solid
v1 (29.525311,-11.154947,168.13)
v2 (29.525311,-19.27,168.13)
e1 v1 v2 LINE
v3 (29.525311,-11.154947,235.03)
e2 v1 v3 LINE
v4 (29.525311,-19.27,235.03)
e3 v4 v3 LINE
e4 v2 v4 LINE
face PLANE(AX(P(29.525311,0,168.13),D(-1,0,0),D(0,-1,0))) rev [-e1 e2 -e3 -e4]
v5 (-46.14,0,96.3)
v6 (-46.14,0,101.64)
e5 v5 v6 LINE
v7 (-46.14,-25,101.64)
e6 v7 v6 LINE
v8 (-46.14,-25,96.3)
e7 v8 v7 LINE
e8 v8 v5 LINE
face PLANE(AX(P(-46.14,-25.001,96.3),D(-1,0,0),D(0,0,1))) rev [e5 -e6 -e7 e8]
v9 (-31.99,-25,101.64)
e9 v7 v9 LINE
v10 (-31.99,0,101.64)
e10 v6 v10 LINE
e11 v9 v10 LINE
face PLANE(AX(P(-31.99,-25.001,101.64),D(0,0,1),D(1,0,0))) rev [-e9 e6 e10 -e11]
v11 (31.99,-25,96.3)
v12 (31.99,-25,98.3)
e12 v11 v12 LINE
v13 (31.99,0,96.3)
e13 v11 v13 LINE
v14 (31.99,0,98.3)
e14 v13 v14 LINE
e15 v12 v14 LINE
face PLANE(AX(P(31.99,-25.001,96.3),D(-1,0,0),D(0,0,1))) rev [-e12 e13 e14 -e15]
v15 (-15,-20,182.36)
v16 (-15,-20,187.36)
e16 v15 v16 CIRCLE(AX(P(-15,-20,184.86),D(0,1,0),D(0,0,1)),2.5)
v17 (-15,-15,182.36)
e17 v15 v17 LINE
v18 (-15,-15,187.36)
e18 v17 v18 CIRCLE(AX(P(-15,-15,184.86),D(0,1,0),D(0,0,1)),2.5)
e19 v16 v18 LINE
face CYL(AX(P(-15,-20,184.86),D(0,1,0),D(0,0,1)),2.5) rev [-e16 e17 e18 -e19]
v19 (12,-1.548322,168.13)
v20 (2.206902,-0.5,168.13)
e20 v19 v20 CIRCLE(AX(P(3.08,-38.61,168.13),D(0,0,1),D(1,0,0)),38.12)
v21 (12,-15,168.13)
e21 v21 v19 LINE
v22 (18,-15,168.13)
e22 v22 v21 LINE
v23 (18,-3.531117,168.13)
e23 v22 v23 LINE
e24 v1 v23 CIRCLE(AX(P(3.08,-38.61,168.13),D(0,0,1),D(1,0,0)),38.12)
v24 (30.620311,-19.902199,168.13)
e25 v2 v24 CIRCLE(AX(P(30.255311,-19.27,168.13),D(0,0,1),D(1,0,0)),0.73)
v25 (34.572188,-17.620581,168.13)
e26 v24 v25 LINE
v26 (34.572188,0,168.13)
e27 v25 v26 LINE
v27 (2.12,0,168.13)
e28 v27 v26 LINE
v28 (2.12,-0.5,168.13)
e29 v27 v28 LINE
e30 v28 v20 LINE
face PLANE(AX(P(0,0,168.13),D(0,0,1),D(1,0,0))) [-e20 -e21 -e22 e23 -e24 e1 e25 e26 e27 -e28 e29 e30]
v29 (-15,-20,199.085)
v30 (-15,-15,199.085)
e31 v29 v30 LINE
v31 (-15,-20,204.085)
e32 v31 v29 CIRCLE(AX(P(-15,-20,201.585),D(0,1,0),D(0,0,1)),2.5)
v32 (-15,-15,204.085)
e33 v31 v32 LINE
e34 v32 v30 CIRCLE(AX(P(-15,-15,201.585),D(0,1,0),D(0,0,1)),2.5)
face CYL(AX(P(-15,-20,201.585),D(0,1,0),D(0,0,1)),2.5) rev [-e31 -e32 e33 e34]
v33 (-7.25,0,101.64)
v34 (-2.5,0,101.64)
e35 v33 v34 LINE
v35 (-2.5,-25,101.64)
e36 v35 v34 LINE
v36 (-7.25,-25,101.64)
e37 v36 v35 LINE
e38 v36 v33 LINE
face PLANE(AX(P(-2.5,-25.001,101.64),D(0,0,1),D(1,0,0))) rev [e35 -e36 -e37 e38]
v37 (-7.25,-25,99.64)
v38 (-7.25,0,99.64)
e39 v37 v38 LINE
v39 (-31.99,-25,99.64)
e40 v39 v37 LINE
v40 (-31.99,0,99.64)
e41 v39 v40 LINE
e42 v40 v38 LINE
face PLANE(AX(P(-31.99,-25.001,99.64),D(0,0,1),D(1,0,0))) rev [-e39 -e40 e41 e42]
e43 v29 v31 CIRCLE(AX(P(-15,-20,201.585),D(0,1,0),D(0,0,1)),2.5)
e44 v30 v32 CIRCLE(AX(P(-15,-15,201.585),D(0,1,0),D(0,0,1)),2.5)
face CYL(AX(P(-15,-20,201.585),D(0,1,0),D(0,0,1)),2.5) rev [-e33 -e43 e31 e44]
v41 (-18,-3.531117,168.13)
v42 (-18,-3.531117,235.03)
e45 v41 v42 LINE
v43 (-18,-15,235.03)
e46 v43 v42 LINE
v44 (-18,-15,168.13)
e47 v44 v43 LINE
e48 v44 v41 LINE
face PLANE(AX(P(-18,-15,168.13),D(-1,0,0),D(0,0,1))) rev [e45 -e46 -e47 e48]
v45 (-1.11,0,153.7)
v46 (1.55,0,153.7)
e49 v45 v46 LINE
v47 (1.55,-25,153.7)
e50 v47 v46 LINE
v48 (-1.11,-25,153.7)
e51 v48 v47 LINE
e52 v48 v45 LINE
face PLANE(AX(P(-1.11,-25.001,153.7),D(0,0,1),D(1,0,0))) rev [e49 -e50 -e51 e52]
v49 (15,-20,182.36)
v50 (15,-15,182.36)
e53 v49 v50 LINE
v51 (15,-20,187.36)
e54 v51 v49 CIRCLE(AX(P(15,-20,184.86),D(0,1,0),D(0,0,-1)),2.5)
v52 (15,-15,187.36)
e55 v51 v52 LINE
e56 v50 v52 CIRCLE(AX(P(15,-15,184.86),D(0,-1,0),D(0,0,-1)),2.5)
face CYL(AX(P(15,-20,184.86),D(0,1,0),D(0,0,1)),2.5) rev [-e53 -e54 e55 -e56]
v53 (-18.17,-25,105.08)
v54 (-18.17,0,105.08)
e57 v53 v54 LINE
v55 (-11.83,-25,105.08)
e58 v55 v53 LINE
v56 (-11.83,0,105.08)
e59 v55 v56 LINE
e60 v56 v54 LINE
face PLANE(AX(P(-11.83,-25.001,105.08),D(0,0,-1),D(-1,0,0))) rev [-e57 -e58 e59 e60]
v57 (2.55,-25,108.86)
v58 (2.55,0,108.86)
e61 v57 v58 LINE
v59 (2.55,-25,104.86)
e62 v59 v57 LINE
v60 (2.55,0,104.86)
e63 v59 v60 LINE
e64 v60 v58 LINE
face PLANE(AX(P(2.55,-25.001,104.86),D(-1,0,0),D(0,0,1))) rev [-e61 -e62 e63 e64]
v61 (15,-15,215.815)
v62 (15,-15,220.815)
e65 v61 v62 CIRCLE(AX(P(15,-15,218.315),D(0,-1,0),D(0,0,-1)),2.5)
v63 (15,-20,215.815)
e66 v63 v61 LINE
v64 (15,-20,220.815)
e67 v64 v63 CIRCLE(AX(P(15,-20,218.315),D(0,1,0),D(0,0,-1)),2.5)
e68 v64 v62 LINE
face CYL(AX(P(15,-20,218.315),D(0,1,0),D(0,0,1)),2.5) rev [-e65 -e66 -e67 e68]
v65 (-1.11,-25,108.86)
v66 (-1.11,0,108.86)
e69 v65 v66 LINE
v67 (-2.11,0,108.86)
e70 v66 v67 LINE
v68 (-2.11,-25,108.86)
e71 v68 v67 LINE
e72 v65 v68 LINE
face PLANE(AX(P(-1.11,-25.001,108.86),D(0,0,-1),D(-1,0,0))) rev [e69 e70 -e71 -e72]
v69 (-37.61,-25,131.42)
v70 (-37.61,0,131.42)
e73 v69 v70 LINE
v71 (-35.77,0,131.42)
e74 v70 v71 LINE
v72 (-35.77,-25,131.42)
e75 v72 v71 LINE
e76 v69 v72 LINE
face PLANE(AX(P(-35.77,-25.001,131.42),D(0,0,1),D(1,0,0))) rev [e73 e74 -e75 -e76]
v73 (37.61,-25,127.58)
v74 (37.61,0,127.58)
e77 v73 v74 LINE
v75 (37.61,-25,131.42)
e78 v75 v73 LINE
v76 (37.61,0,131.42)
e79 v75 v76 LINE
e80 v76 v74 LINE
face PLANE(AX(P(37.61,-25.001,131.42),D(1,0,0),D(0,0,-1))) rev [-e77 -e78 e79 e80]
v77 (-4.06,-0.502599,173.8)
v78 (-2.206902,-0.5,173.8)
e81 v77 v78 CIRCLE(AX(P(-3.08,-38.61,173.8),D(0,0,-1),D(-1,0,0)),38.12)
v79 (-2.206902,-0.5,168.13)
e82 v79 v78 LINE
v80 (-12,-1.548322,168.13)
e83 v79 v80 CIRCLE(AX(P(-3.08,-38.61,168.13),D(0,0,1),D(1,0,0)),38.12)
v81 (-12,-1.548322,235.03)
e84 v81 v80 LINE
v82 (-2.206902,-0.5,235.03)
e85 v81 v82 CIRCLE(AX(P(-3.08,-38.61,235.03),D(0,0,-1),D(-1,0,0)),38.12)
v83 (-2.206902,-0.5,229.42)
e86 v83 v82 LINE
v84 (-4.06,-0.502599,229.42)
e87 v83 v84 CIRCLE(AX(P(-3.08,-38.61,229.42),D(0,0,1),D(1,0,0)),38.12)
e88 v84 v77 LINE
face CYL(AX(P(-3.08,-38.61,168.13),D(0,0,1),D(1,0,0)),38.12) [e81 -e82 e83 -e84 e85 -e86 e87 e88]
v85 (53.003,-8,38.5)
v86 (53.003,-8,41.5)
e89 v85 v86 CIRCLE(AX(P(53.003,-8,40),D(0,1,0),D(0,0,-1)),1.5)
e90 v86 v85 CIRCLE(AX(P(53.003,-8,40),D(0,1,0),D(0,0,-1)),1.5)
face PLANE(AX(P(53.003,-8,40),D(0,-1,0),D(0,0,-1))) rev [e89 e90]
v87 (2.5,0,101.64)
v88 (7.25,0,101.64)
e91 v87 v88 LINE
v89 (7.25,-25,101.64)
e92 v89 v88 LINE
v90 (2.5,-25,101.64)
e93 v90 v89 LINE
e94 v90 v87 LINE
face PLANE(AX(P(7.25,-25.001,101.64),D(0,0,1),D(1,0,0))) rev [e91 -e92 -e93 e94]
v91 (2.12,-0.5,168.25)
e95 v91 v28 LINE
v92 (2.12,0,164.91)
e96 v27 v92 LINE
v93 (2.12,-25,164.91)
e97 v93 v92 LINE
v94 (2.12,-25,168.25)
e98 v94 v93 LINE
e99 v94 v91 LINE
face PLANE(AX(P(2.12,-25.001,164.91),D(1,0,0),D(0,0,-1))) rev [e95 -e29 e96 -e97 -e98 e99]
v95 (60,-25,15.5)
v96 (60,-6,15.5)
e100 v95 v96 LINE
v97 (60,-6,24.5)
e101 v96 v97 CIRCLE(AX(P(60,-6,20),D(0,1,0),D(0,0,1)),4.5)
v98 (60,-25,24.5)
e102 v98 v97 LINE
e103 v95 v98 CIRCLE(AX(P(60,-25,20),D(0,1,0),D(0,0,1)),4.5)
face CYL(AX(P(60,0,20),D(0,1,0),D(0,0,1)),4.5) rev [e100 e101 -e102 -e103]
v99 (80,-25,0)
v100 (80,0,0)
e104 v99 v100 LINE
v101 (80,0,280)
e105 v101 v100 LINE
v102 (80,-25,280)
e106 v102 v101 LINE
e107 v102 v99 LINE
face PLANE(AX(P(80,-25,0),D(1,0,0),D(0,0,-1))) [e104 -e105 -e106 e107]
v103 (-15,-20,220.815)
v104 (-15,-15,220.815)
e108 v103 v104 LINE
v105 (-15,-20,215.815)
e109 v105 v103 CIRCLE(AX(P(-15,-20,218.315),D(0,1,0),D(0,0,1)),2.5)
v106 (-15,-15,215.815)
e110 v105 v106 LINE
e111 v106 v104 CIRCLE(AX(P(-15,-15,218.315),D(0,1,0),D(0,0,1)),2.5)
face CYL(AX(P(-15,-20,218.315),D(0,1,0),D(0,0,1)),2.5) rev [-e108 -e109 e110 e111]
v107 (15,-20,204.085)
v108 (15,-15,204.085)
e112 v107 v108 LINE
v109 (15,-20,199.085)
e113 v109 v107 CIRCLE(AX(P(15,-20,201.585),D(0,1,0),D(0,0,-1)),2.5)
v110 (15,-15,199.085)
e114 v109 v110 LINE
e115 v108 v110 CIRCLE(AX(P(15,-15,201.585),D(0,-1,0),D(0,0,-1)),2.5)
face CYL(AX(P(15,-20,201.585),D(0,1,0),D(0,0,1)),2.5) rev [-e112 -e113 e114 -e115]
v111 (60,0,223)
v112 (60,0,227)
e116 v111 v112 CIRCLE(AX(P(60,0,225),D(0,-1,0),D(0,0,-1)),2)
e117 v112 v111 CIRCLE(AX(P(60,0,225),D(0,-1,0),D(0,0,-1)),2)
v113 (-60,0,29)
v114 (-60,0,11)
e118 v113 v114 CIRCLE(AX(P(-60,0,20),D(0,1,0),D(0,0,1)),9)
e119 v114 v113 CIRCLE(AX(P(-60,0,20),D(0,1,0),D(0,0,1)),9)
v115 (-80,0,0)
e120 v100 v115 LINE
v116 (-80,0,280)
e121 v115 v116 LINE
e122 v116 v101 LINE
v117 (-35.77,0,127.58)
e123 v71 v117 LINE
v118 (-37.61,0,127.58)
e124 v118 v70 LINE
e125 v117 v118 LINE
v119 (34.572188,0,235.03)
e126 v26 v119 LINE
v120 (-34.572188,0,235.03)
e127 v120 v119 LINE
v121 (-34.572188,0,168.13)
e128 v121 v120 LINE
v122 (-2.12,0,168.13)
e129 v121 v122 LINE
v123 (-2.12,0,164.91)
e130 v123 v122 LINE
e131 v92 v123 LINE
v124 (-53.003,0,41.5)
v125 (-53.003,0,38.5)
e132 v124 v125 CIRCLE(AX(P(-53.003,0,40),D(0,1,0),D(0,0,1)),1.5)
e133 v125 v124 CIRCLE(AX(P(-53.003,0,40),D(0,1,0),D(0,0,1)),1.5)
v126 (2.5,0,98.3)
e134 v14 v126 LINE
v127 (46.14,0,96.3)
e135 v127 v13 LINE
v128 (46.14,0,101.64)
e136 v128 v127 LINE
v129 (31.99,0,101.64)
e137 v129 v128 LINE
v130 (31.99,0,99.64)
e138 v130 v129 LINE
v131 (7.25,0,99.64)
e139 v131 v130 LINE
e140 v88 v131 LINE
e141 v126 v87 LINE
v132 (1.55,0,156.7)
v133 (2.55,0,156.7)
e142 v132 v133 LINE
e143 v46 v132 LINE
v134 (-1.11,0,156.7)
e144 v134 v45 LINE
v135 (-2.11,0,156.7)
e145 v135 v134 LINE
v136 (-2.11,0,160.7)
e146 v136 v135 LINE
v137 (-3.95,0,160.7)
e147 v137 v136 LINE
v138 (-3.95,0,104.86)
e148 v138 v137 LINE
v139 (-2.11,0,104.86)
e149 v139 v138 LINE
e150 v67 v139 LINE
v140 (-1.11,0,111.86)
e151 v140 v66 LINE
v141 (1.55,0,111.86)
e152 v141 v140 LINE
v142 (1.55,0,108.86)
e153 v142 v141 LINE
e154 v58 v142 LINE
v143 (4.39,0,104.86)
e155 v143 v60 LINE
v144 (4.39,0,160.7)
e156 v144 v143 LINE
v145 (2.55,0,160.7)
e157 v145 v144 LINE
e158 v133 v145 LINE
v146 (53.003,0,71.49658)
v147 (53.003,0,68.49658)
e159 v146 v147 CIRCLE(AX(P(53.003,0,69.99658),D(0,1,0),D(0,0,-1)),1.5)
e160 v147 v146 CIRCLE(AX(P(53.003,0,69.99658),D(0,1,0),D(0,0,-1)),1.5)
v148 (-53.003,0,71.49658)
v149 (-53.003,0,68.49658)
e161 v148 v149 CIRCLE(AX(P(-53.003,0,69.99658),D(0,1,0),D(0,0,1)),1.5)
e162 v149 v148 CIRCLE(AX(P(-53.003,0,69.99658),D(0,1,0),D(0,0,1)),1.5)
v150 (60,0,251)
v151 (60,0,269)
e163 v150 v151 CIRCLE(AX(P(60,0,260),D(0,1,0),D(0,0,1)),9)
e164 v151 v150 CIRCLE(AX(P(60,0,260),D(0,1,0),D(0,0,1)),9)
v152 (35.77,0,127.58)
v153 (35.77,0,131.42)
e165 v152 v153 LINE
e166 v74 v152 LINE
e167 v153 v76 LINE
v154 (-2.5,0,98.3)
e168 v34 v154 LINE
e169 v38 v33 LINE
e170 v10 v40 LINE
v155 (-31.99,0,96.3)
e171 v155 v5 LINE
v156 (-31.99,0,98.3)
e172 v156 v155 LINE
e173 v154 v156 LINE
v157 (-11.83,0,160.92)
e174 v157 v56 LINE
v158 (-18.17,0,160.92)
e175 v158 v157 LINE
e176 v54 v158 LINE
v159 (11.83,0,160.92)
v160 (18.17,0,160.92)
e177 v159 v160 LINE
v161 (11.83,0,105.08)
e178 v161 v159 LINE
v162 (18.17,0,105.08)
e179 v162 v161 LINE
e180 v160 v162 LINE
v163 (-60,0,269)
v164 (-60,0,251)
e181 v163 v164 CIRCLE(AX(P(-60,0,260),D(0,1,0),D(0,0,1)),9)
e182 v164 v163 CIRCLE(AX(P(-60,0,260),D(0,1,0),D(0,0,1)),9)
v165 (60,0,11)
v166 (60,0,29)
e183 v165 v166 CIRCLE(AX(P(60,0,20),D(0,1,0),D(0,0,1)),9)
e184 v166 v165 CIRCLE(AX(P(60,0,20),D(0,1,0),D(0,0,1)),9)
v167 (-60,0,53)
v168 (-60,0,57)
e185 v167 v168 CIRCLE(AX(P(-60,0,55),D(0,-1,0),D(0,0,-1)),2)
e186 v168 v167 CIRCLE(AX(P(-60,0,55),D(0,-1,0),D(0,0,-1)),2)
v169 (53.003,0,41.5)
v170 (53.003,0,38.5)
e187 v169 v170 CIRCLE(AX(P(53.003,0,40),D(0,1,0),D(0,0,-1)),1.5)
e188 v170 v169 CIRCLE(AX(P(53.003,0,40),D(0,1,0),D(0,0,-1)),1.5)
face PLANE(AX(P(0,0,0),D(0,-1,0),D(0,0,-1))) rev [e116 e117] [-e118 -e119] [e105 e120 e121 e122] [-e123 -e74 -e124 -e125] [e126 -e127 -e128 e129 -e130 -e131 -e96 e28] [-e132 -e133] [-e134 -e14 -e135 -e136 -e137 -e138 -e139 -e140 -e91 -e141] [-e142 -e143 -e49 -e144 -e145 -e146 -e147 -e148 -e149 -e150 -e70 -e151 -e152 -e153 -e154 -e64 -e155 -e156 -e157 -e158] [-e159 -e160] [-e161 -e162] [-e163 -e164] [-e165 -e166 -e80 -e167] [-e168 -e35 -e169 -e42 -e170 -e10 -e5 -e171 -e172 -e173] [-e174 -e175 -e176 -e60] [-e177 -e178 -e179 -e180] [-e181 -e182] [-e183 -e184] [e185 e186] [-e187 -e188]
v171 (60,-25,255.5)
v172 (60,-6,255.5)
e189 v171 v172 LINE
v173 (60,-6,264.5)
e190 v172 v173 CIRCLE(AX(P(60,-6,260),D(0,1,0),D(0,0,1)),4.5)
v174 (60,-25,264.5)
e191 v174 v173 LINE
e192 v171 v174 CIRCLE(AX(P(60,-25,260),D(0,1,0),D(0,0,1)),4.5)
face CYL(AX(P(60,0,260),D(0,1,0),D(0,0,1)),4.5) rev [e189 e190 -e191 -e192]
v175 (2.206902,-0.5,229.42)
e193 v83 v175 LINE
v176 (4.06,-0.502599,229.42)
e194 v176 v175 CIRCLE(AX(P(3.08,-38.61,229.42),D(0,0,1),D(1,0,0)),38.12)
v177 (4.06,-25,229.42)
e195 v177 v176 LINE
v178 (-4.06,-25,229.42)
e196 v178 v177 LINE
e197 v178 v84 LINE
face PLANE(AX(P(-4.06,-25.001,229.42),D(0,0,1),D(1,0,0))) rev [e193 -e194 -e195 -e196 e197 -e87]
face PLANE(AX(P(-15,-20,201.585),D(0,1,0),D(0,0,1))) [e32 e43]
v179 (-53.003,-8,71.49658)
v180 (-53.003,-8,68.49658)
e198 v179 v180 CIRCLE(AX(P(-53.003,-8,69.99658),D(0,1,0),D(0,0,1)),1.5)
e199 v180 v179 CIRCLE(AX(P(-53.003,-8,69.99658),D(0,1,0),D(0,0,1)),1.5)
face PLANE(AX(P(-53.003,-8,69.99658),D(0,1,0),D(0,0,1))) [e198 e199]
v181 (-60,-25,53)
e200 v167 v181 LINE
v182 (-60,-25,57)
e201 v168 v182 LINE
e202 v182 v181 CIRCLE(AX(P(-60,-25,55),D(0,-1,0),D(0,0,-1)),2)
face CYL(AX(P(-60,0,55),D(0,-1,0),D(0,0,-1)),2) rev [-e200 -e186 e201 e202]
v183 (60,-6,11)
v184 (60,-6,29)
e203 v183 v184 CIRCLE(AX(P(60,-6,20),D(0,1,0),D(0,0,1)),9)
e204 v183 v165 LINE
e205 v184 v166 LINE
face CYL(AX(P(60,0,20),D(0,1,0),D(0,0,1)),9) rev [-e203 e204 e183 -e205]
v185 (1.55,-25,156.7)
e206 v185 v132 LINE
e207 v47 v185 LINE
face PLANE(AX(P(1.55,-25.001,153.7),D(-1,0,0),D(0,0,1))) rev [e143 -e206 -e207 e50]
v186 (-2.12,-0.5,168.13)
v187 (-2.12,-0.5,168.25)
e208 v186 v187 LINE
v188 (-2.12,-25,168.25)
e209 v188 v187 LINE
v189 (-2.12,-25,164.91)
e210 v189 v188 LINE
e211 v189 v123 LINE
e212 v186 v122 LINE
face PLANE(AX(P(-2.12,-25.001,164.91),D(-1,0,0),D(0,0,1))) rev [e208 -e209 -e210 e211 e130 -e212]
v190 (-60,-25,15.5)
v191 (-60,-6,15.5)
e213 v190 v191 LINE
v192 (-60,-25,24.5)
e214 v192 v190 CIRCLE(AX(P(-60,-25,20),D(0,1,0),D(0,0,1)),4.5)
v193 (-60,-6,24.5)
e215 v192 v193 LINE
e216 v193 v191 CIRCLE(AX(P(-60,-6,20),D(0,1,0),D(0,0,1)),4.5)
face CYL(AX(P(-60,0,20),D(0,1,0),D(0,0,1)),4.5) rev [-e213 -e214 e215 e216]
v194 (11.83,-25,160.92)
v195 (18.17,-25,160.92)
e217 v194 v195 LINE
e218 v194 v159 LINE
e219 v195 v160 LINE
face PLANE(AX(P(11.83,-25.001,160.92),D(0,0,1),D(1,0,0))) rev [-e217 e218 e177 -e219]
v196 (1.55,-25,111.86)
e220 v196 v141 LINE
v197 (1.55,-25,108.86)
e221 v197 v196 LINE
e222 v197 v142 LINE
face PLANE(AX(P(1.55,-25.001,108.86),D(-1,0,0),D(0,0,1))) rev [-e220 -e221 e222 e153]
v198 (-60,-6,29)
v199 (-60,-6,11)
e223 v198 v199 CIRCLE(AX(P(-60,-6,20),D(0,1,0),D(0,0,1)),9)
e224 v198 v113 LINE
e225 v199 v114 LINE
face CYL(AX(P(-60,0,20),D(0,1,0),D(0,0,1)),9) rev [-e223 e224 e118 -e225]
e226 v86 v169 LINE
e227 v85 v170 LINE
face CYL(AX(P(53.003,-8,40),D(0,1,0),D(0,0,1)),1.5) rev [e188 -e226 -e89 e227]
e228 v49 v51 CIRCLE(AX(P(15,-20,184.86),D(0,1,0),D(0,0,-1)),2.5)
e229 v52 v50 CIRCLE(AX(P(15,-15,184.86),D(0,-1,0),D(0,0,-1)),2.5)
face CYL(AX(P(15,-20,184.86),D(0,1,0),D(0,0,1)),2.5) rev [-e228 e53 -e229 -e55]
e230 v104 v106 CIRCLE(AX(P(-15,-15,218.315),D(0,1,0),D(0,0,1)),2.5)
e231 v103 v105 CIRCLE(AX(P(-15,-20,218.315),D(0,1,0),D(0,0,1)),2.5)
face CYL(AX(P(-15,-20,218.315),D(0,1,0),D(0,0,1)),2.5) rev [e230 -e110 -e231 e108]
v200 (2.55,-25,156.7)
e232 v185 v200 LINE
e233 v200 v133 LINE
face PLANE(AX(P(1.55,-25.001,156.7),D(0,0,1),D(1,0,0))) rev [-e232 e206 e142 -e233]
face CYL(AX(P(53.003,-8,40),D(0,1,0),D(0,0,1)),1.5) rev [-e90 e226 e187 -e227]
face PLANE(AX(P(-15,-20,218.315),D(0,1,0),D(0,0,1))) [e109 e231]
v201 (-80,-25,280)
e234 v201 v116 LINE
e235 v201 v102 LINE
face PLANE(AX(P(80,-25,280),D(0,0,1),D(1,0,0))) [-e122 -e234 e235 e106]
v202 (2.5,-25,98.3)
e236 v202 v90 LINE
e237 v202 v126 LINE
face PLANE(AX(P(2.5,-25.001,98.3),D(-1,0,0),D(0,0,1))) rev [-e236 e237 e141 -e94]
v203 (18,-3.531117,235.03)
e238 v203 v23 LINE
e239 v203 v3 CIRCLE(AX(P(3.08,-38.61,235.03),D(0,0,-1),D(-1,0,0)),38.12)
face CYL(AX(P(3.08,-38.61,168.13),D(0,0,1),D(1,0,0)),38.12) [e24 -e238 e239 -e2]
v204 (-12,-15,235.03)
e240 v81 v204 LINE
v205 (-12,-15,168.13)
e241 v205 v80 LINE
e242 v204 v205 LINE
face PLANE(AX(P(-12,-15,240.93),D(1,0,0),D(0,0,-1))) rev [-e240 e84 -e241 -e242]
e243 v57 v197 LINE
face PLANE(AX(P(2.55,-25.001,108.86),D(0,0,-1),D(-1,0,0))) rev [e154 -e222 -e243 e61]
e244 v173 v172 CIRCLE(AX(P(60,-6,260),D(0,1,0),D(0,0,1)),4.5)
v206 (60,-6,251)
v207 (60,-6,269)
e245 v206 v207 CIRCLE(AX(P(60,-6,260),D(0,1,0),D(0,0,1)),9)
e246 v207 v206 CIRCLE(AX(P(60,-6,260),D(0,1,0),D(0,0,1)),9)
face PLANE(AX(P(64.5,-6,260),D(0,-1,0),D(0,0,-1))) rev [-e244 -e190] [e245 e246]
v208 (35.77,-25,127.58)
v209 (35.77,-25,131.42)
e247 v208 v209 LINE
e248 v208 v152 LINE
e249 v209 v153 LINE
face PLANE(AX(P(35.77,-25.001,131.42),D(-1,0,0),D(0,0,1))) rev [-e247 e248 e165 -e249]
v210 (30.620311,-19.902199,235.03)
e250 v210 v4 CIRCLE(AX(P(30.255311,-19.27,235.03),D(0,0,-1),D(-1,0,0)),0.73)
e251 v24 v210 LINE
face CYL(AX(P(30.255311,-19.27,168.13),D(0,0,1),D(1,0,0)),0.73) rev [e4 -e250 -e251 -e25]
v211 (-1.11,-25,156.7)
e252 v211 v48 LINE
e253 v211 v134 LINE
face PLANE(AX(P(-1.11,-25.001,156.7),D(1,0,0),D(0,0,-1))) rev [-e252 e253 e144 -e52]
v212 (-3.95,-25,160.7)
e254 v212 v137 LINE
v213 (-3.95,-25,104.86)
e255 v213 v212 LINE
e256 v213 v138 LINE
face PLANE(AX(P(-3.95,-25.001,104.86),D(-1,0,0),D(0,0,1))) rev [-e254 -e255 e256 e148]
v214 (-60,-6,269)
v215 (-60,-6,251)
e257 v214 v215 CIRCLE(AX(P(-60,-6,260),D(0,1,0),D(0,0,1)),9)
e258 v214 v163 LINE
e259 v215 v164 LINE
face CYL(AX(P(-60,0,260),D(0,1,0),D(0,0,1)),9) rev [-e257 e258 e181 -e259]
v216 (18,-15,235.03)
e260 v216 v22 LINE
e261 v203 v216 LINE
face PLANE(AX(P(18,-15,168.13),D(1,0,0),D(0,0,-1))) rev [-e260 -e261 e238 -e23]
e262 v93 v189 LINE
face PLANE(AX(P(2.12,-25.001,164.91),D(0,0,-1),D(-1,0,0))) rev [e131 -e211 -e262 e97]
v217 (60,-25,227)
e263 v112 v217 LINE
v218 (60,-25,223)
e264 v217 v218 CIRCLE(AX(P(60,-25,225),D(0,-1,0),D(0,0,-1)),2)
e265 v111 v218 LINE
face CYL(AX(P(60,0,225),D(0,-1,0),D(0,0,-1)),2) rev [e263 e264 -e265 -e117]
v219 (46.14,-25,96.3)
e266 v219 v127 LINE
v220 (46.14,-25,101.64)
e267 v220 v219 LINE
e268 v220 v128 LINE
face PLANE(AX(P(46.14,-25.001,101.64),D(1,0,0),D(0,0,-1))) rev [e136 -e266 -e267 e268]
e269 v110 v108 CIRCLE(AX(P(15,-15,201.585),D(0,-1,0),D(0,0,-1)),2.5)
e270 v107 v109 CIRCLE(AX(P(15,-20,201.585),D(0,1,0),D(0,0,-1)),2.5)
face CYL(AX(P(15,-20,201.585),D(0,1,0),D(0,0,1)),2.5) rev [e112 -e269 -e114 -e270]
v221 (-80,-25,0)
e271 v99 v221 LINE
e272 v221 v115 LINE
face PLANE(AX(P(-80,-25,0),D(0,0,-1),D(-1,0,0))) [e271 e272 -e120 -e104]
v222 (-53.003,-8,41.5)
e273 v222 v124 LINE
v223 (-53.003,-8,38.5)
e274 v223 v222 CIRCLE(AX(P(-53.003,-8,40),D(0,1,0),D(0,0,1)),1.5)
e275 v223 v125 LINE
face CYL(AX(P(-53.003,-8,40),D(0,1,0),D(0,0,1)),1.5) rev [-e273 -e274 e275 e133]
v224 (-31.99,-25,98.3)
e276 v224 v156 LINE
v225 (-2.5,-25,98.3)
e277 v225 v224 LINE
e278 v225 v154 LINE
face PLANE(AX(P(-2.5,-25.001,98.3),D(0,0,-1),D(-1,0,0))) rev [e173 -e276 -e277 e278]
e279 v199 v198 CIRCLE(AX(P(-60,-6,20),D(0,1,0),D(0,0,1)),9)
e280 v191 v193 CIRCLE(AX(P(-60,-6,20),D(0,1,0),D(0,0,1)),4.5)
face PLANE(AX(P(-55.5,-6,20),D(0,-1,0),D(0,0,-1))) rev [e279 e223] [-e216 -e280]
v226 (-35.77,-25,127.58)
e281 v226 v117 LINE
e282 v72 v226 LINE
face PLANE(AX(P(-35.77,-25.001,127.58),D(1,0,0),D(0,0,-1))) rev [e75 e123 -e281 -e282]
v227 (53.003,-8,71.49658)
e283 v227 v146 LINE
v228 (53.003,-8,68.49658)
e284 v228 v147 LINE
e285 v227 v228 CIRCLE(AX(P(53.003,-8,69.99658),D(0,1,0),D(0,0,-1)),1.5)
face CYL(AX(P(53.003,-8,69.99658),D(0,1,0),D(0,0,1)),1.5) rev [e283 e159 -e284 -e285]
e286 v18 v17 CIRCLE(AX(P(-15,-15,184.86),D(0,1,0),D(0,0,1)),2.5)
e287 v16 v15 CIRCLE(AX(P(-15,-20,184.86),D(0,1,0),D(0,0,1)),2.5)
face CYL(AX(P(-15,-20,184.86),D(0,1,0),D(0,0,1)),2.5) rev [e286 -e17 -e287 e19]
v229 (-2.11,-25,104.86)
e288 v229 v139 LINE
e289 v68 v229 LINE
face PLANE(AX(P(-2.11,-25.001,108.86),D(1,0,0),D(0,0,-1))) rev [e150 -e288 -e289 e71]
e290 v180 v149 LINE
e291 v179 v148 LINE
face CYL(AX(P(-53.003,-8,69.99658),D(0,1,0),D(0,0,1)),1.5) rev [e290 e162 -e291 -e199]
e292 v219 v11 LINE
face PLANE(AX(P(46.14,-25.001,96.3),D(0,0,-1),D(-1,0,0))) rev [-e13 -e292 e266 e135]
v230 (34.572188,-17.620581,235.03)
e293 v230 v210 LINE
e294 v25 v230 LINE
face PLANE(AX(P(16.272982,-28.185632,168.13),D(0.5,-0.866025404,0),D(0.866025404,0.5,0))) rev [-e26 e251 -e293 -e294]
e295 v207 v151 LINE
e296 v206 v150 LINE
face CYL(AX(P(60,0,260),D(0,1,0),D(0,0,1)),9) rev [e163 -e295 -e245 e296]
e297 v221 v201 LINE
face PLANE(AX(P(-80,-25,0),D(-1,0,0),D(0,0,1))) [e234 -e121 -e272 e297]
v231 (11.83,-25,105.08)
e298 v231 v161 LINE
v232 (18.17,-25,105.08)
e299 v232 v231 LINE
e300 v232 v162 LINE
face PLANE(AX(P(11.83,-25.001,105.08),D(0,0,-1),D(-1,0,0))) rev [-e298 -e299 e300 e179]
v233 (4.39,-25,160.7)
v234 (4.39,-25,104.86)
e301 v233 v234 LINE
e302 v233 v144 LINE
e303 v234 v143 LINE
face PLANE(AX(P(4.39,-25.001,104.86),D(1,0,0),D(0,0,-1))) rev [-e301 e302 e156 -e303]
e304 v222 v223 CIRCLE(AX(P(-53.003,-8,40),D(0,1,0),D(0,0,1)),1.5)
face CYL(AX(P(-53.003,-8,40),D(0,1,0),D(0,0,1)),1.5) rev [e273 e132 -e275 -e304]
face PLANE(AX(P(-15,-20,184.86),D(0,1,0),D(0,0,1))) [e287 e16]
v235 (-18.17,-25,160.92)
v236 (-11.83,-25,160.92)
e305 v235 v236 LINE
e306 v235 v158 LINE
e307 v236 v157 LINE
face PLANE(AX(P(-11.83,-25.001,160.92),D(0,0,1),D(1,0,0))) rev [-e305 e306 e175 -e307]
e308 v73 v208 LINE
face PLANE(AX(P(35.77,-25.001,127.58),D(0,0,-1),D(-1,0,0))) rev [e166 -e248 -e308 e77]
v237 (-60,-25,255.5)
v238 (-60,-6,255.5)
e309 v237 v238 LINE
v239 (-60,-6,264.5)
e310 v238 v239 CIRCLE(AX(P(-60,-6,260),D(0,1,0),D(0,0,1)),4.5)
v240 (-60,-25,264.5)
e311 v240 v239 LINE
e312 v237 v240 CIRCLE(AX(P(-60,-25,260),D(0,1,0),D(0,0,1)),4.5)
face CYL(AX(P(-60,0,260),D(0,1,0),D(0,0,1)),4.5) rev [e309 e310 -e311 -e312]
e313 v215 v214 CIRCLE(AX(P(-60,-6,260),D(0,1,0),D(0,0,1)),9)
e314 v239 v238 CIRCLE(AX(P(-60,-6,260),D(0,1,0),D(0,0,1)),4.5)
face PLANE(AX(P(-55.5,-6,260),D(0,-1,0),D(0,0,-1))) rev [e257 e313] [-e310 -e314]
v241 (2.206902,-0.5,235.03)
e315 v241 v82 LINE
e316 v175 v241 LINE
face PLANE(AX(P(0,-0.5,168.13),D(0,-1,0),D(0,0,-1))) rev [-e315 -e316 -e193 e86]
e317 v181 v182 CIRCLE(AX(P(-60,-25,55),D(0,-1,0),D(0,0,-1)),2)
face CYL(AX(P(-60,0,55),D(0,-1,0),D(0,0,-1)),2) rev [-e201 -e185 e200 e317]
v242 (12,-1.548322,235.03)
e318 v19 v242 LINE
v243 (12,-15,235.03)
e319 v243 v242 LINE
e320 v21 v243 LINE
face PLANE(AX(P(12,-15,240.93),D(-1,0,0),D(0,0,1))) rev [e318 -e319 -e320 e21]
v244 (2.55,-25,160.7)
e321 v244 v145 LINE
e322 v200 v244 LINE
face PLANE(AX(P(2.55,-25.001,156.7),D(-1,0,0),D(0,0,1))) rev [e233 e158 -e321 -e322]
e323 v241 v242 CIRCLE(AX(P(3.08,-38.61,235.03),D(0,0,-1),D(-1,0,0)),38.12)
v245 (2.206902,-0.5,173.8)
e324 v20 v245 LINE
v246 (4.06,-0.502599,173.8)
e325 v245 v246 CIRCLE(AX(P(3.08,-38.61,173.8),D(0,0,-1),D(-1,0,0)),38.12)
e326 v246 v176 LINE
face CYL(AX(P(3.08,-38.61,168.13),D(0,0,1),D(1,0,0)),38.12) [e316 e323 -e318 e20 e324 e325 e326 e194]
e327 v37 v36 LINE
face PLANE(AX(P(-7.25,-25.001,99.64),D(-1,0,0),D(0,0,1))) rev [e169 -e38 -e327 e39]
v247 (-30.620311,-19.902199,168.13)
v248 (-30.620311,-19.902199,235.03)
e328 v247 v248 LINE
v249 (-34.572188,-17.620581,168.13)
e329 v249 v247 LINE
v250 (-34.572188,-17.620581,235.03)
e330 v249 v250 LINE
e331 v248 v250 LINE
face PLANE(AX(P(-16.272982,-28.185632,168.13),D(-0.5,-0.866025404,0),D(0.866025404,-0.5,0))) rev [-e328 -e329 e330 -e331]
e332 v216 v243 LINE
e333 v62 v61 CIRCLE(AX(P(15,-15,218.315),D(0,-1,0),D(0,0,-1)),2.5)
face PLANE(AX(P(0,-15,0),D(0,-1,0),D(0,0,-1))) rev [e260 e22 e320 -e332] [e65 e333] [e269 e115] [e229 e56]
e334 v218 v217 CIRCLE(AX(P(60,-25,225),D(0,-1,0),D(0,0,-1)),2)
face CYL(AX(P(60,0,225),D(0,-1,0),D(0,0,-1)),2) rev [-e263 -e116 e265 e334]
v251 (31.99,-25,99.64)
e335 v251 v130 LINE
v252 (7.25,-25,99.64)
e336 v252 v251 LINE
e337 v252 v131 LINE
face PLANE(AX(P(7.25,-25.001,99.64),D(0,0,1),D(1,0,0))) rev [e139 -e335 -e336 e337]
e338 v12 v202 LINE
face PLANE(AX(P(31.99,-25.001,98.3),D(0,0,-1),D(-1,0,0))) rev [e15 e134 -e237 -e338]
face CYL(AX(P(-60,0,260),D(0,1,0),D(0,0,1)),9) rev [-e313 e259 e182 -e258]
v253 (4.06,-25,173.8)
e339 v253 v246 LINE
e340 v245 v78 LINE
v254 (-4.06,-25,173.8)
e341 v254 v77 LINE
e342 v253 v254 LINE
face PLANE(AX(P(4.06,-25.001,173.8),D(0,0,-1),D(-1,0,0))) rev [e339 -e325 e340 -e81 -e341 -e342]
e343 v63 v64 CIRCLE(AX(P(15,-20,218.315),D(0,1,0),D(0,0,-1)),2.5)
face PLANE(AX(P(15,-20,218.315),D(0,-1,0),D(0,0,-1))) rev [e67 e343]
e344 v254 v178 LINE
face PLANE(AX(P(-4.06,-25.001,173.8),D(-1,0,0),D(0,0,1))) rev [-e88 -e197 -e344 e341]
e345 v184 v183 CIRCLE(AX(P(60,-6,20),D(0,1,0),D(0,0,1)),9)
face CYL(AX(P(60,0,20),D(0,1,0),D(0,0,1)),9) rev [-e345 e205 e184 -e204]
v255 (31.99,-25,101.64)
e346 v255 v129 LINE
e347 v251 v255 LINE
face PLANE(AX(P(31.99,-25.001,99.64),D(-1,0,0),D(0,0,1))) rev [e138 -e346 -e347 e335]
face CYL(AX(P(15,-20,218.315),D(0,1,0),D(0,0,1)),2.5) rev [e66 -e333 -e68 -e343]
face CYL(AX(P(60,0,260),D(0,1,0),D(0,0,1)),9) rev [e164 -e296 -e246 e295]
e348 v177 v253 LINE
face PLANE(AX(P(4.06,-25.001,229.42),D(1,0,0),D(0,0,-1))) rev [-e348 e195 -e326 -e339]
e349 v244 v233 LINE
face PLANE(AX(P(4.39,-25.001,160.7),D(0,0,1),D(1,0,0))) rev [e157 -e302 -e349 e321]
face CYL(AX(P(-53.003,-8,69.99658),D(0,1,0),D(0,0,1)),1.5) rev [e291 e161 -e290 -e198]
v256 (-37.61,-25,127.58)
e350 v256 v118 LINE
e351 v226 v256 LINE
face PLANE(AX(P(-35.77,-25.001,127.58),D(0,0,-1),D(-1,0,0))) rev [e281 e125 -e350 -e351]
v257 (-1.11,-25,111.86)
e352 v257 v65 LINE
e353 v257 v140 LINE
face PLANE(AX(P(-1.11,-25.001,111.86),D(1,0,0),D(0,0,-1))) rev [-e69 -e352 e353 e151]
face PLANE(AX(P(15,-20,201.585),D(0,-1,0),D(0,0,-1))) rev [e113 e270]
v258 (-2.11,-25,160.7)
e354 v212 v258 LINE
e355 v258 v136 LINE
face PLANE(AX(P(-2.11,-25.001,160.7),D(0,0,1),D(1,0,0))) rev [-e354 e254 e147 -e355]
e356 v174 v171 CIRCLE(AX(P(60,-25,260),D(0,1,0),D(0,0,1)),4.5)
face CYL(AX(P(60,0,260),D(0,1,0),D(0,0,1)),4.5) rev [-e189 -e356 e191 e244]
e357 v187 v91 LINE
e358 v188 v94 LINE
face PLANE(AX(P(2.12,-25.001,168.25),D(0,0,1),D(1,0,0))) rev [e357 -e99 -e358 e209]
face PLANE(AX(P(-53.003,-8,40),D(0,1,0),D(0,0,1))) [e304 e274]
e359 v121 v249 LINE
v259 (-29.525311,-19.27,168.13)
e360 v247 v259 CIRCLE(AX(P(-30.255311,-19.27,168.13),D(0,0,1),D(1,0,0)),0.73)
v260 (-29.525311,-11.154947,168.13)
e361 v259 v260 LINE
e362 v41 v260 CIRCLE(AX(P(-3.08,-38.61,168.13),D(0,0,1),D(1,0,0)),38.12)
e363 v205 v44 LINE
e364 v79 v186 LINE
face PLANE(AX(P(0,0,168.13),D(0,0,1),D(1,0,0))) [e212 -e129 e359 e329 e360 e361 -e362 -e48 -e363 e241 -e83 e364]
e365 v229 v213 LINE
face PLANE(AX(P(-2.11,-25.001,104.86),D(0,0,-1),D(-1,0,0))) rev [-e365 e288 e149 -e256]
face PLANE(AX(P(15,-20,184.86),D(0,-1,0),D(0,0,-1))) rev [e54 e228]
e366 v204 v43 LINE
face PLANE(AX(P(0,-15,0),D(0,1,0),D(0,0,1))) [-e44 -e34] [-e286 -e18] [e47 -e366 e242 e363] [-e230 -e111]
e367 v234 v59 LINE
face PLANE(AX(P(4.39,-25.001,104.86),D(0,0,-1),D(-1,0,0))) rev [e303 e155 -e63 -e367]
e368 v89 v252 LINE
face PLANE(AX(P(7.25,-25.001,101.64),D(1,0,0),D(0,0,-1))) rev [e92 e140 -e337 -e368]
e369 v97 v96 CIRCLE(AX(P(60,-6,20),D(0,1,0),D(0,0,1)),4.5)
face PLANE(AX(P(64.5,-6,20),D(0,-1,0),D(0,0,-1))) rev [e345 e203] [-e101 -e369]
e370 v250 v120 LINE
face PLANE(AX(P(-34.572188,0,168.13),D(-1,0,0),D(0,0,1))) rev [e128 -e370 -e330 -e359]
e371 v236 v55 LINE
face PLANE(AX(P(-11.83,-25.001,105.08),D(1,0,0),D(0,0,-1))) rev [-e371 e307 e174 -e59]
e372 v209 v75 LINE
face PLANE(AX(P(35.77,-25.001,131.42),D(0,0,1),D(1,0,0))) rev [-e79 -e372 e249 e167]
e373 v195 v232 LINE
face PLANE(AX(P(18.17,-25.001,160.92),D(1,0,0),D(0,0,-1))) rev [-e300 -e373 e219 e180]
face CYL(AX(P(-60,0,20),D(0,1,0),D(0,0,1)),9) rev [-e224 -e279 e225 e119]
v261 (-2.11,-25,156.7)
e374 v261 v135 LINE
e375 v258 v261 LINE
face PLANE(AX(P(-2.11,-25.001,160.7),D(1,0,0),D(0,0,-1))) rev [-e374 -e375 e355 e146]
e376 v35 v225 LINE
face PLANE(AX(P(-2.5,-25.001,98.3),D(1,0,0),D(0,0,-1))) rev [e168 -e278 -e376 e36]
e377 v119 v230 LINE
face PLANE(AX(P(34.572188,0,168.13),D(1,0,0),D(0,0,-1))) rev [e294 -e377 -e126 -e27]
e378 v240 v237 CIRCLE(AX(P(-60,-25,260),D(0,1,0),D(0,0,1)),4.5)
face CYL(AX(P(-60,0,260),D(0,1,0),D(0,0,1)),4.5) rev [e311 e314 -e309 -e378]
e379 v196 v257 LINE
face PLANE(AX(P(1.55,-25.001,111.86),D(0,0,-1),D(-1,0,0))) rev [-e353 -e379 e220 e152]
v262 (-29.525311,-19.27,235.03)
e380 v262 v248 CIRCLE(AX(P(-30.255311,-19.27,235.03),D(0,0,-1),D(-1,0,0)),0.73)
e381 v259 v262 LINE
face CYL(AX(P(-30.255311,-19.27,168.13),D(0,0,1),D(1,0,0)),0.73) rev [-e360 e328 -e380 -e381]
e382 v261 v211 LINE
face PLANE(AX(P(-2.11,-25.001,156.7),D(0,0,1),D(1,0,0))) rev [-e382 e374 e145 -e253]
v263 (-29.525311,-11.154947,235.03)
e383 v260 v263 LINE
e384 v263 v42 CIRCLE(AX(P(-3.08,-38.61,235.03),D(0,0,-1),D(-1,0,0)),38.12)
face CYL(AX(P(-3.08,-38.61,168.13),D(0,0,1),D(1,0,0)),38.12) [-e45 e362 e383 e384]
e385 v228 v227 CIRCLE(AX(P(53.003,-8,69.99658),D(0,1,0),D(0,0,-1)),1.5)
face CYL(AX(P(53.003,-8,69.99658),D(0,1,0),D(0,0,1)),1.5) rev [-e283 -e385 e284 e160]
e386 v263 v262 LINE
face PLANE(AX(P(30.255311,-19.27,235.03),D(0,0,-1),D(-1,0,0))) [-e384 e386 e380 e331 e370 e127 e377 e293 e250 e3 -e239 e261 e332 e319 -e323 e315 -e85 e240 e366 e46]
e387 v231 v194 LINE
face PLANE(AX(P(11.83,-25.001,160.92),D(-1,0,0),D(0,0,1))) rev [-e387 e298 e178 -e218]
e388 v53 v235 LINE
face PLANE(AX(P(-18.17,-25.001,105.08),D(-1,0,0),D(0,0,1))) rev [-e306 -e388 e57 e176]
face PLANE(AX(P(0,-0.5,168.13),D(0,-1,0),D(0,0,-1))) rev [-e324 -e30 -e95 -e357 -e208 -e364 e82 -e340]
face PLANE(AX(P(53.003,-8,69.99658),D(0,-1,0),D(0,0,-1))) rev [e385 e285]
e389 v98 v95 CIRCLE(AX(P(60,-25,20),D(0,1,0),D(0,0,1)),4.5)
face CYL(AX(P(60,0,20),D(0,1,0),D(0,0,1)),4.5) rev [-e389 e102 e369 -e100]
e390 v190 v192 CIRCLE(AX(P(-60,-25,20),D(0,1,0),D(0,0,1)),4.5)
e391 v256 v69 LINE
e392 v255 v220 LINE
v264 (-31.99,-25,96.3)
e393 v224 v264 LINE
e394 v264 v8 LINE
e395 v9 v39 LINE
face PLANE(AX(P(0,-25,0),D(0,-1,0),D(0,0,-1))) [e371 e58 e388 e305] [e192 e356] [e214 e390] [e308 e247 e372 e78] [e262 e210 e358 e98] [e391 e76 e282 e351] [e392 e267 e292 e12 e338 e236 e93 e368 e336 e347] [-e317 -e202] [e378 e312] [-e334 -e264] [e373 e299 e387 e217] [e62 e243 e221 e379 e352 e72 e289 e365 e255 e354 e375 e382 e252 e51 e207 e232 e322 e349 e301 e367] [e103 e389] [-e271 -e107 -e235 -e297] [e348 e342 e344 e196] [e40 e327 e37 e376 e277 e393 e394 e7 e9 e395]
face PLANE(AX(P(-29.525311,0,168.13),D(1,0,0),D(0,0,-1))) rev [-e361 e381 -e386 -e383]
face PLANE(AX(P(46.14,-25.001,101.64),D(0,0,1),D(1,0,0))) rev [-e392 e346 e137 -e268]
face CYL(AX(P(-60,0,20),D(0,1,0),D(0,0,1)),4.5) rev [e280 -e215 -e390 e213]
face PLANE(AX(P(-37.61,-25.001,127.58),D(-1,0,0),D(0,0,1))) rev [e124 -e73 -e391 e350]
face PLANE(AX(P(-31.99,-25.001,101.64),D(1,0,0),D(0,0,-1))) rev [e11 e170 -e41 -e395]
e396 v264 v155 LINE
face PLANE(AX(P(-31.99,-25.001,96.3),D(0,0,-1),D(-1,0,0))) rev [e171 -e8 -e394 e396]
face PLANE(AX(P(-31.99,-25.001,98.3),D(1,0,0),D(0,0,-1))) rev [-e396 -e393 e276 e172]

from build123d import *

# Parameters (mm, degrees)
SKETCH1_W                                        = 160
SKETCH1_H                                        = 280
BOSS_EXTRUDE1_DEPTH                              = 25
CBORE_FOR_M8_PAN_HEAD_MACHINE_SCREW1_D           = 9
CBORE_FOR_M8_PAN_HEAD_MACHINE_SCREW1_CBORE_D     = 18
CBORE_FOR_M8_PAN_HEAD_MACHINE_SCREW1_CBORE_DEPTH = 6
CUT_EXTRUDE2_DEPTH                               = 72.8
CUT_EXTRUDE4_REACH                               = 294.276
SKETCH_5_W                                       = 4.24
SKETCH_5_H                                       = 3.34
SKETCH_5_W_2                                     = 8.12
SKETCH_5_H_2                                     = 55.62
SKETCH_5_W_3                                     = 1.84
SKETCH_5_H_3                                     = 3.84
SKETCH_5_W_4                                     = 6.34
SKETCH_5_H_4                                     = 55.84
SKETCH_6_W                                       = 6
SKETCH_6_H                                       = 72.8
CUT_EXTRUDE5_DEPTH                               = 15
EXTRUDE_1_DEPTH                                  = 5.9
SKETCH10_R                                       = 2.5
CUT_EXTRUDE6_DEPTH                               = 20
SKETCH13_R                                       = 1.5
CUT_EXTRUDE7_DEPTH                               = 8
SKETCH14_R                                       = 2
CUT_EXTRUDE8_DEPTH                               = 293.275554914


with BuildPart() as part:
    # Sketch1 → Boss-Extrude1 (new body)
    with BuildSketch(Plane(origin=(0, 0, 0), x_dir=(1, 0, 0), z_dir=(0, 1, 0))):
        with Locations((0, -140)):
            Rectangle(SKETCH1_W, SKETCH1_H)
    extrude(amount=-BOSS_EXTRUDE1_DEPTH)

    # CBORE for M8 Pan Head Machine Screw1 (through all)
    with Locations(Plane(origin=(0, 0, 0), x_dir=(1, 0, 0), z_dir=(0, 1, 0))):
        with Locations((-60, -260), (60, -260), (60, -20), (-60, -20)):
            CounterBoreHole(CBORE_FOR_M8_PAN_HEAD_MACHINE_SCREW1_D / 2, CBORE_FOR_M8_PAN_HEAD_MACHINE_SCREW1_CBORE_D / 2, CBORE_FOR_M8_PAN_HEAD_MACHINE_SCREW1_CBORE_DEPTH)

    # Sketch4 → Cut-Extrude2 (cut)
    with BuildSketch(Plane.XY.offset(240.93)):
        with BuildLine():
            ThreePointArc((29.525310886, -11.154947057), (16.931588105, -3.095666176), (2.206902067, -0.5))
            Line((2.206902067, -0.5), (-2.206902067, -0.5))
            ThreePointArc((-2.206902067, -0.5), (-16.931588105, -3.095666176), (-29.525310886, -11.154947057))
            Line((-29.525310886, -11.154947057), (-29.525310886, -19.27))
            ThreePointArc((-29.525310886, -19.27), (-29.890310886, -19.902198545), (-30.620310886, -19.902198545))
            Line((-30.620310886, -19.902198545), (-34.572188183, -17.620581124))
            Line((-34.572188183, -17.620581124), (-34.572188183, 0))
            Line((-34.572188183, 0), (34.572188183, 0))
            Line((34.572188183, 0), (34.572188183, -17.620581124))
            Line((34.572188183, -17.620581124), (30.620310886, -19.902198545))
            ThreePointArc((30.620310886, -19.902198545), (29.890310886, -19.902198545), (29.525310886, -19.27))
            Line((29.525310886, -19.27), (29.525310886, -11.154947057))
        make_face()
    extrude(amount=-CUT_EXTRUDE2_DEPTH, mode=Mode.SUBTRACT)

    # 草图5 → Cut-Extrude4 (cut, up to next)
    with BuildSketch(Plane(origin=(0, 0, 0), x_dir=(1, 0, 0), z_dir=(0, 1, 0)), mode=Mode.PRIVATE) as cut_extrude4_sk1:
        with Locations((0, -166.58)):
            Rectangle(SKETCH_5_W, SKETCH_5_H)
    cut_extrude4_tool1 = extrude(cut_extrude4_sk1.sketch, amount=-CUT_EXTRUDE4_REACH, mode=Mode.PRIVATE) & part.part
    # 草图5 → Cut-Extrude4 (cut, up to next)
    with BuildSketch(Plane(origin=(0, 0, 0), x_dir=(1, 0, 0), z_dir=(0, 1, 0)), mode=Mode.PRIVATE) as cut_extrude4_sk2:
        with Locations((0, -201.61)):
            Rectangle(SKETCH_5_W_2, SKETCH_5_H_2)
    cut_extrude4_tool2 = extrude(cut_extrude4_sk2.sketch, amount=-CUT_EXTRUDE4_REACH, mode=Mode.PRIVATE) & part.part
    # 草图5 → Cut-Extrude4 (cut, up to next)
    with BuildSketch(Plane(origin=(0, 0, 0), x_dir=(1, 0, 0), z_dir=(0, 1, 0)), mode=Mode.PRIVATE) as cut_extrude4_sk3:
        with Locations((36.69, -129.5)):
            Rectangle(SKETCH_5_W_3, SKETCH_5_H_3)
    cut_extrude4_tool3 = extrude(cut_extrude4_sk3.sketch, amount=-CUT_EXTRUDE4_REACH, mode=Mode.PRIVATE) & part.part
    # 草图5 → Cut-Extrude4 (cut, up to next)
    with BuildSketch(Plane(origin=(0, 0, 0), x_dir=(1, 0, 0), z_dir=(0, 1, 0)), mode=Mode.PRIVATE) as cut_extrude4_sk4:
        with Locations((15, -133)):
            Rectangle(SKETCH_5_W_4, SKETCH_5_H_4)
    cut_extrude4_tool4 = extrude(cut_extrude4_sk4.sketch, amount=-CUT_EXTRUDE4_REACH, mode=Mode.PRIVATE) & part.part
    # 草图5 → Cut-Extrude4 (cut, up to next)
    with BuildSketch(Plane(origin=(0, 0, 0), x_dir=(1, 0, 0), z_dir=(0, 1, 0)), mode=Mode.PRIVATE) as cut_extrude4_sk5:
        Polygon((4.39, -104.86), (4.39, -160.7), (2.55, -160.7), (2.55, -156.7), (1.55, -156.7), (1.55, -153.7), (-1.11, -153.7), (-1.11, -156.7), (-2.11, -156.7), (-2.11, -160.7), (-3.95, -160.7), (-3.95, -104.86), (-2.11, -104.86), (-2.11, -108.86), (-1.11, -108.86), (-1.11, -111.86), (1.55, -111.86), (1.55, -108.86), (2.55, -108.86), (2.55, -104.86), align=None)
    cut_extrude4_tool5 = extrude(cut_extrude4_sk5.sketch, amount=-CUT_EXTRUDE4_REACH, mode=Mode.PRIVATE) & part.part
    # 草图5 → Cut-Extrude4 (cut, up to next)
    with BuildSketch(Plane(origin=(0, 0, 0), x_dir=(1, 0, 0), z_dir=(0, 1, 0)), mode=Mode.PRIVATE) as cut_extrude4_sk6:
        with Locations((-15, -133)):
            Rectangle(SKETCH_5_W_4, SKETCH_5_H_4)
    cut_extrude4_tool6 = extrude(cut_extrude4_sk6.sketch, amount=-CUT_EXTRUDE4_REACH, mode=Mode.PRIVATE) & part.part
    # 草图5 → Cut-Extrude4 (cut, up to next)
    with BuildSketch(Plane(origin=(0, 0, 0), x_dir=(1, 0, 0), z_dir=(0, 1, 0)), mode=Mode.PRIVATE) as cut_extrude4_sk7:
        with Locations((-36.69, -129.5)):
            Rectangle(SKETCH_5_W_3, SKETCH_5_H_3)
    cut_extrude4_tool7 = extrude(cut_extrude4_sk7.sketch, amount=-CUT_EXTRUDE4_REACH, mode=Mode.PRIVATE) & part.part
    # 草图5 → Cut-Extrude4 (cut, up to next)
    with BuildSketch(Plane(origin=(0, 0, 0), x_dir=(1, 0, 0), z_dir=(0, 1, 0)), mode=Mode.PRIVATE) as cut_extrude4_sk8:
        Polygon((7.25, -101.64), (2.5, -101.64), (2.5, -98.3), (31.99, -98.3), (31.99, -96.3), (46.14, -96.3), (46.14, -101.64), (31.99, -101.64), (31.99, -99.64), (7.25, -99.64), align=None)
    cut_extrude4_tool8 = extrude(cut_extrude4_sk8.sketch, amount=-CUT_EXTRUDE4_REACH, mode=Mode.PRIVATE) & part.part
    # 草图5 → Cut-Extrude4 (cut, up to next)
    with BuildSketch(Plane(origin=(0, 0, 0), x_dir=(1, 0, 0), z_dir=(0, 1, 0)), mode=Mode.PRIVATE) as cut_extrude4_sk9:
        Polygon((-2.5, -98.3), (-31.99, -98.3), (-31.99, -96.3), (-46.14, -96.3), (-46.14, -101.64), (-31.99, -101.64), (-31.99, -99.64), (-7.25, -99.64), (-7.25, -101.64), (-2.5, -101.64), align=None)
    cut_extrude4_tool9 = extrude(cut_extrude4_sk9.sketch, amount=-CUT_EXTRUDE4_REACH, mode=Mode.PRIVATE) & part.part
    add(cut_extrude4_tool1.solids().sort_by_distance((0, 0, 166.58))[0], mode=Mode.SUBTRACT)
    add(cut_extrude4_tool2.solids().sort_by_distance((0, 0, 201.61))[0], mode=Mode.SUBTRACT)
    add(cut_extrude4_tool3.solids().sort_by_distance((36.69, 0, 129.5))[0], mode=Mode.SUBTRACT)
    add(cut_extrude4_tool4.solids().sort_by_distance((15, 0, 133))[0], mode=Mode.SUBTRACT)
    add(cut_extrude4_tool5.solids().sort_by_distance((0.22, 0, 132.78))[0], mode=Mode.SUBTRACT)
    add(cut_extrude4_tool6.solids().sort_by_distance((-15, 0, 133))[0], mode=Mode.SUBTRACT)
    add(cut_extrude4_tool7.solids().sort_by_distance((-36.69, 0, 129.5))[0], mode=Mode.SUBTRACT)
    add(cut_extrude4_tool8.solids().sort_by_distance((29.536343, 0, 99.09735))[0], mode=Mode.SUBTRACT)
    add(cut_extrude4_tool9.solids().sort_by_distance((-29.536343, 0, 99.09735))[0], mode=Mode.SUBTRACT)

    # 草图6 → Cut-Extrude5 (cut)
    with BuildSketch(Plane(origin=(0, 0, 0), x_dir=(1, 0, 0), z_dir=(0, 1, 0))):
        with Locations((-15, -204.53)):
            Rectangle(SKETCH_6_W, SKETCH_6_H)
        with Locations((15, -204.53)):
            Rectangle(SKETCH_6_W, SKETCH_6_H)
    extrude(amount=-CUT_EXTRUDE5_DEPTH, mode=Mode.SUBTRACT)

    # Sketch7 → 凸台-拉伸1 (add)
    with BuildSketch(Plane(origin=(0, 0, 240.93), x_dir=(-1, 0, 0), z_dir=(0, 0, -1))):
        with BuildLine():
            Line((-18, -3.531117464), (-18, -15))
            Line((-18, -15), (-12, -15))
            Line((-12, -15), (-12, -1.548321679))
            ThreePointArc((-12, -1.548321679), (-7.137450284, -0.706550326), (-2.206902067, -0.5))
            Line((-2.206902067, -0.5), (2.206902067, -0.5))
            ThreePointArc((2.206902067, -0.5), (7.137450284, -0.706550326), (12, -1.548321679))
            Line((12, -1.548321679), (12, -15))
            Line((12, -15), (18, -15))
            Line((18, -15), (18, -3.531117464))
            ThreePointArc((18, -3.531117464), (24.110999277, -6.816424086), (29.525310886, -11.154947057))
            Line((29.525310886, -11.154947057), (29.525310886, -19.27))
            ThreePointArc((29.525310886, -19.27), (29.890310886, -19.902198545), (30.620310886, -19.902198545))
            Line((30.620310886, -19.902198545), (34.572188183, -17.620581124))
            Line((34.572188183, -17.620581124), (34.572188183, 0))
            Line((34.572188183, 0), (-34.572188183, 0))
            Line((-34.572188183, 0), (-34.572188183, -17.620581124))
            Line((-34.572188183, -17.620581124), (-30.620310886, -19.902198545))
            ThreePointArc((-30.620310886, -19.902198545), (-29.890310886, -19.902198545), (-29.525310886, -19.27))
            Line((-29.525310886, -19.27), (-29.525310886, -11.154947057))
            ThreePointArc((-29.525310886, -11.154947057), (-24.110999277, -6.816424086), (-18, -3.531117464))
        make_face()
    extrude(amount=EXTRUDE_1_DEPTH)

    # Sketch10 → Cut-Extrude6 (cut)
    with BuildSketch(Plane(origin=(0, 0, 0), x_dir=(1, 0, 0), z_dir=(0, 1, 0))):
        with Locations(Location((-15, -184.86, 0), (0, 0, 270))):
            Circle(SKETCH10_R)
        with Locations(Location((-15, -218.315, 0), (0, 0, 270))):
            Circle(SKETCH10_R)
        with Locations(Location((-15, -201.585, 0), (0, 0, 270))):
            Circle(SKETCH10_R)
        with Locations(Location((15, -218.315, 0), (0, 0, 90))):
            Circle(SKETCH10_R)
        with Locations(Location((15, -201.585, 0), (0, 0, 90))):
            Circle(SKETCH10_R)
        with Locations(Location((15, -184.86, 0), (0, 0, 90))):
            Circle(SKETCH10_R)
    extrude(amount=-CUT_EXTRUDE6_DEPTH, mode=Mode.SUBTRACT)

    # Sketch13 → Cut-Extrude7 (cut)
    with BuildSketch(Plane(origin=(0, 0, 0), x_dir=(1, 0, 0), z_dir=(0, 1, 0))):
        with Locations(Location((-53.003, -40, 0), (0, 0, 270))):
            Circle(SKETCH13_R)
        with Locations(Location((-53.003, -69.996579655, 0), (0, 0, 270))):
            Circle(SKETCH13_R)
        with Locations(Location((53.003, -69.996579655, 0), (0, 0, 90))):
            Circle(SKETCH13_R)
        with Locations(Location((53.003, -40, 0), (0, 0, 90))):
            Circle(SKETCH13_R)
        Polygon((7.25, -99.64), (31.99, -99.64), (31.99, -101.64), (46.14, -101.64), (46.14, -96.3), (31.99, -96.3), (31.99, -98.3), (2.5, -98.3), (2.5, -101.64), (7.25, -101.64), align=None)
        Polygon((-2.5, -98.3), (-31.99, -98.3), (-31.99, -96.3), (-46.14, -96.3), (-46.14, -101.64), (-31.99, -101.64), (-31.99, -99.64), (-7.25, -99.64), (-7.25, -101.64), (-2.5, -101.64), align=None)
    extrude(amount=-CUT_EXTRUDE7_DEPTH, mode=Mode.SUBTRACT)

    # Sketch14 → Cut-Extrude8 (cut, through all)
    with BuildSketch(Plane.XZ.offset(25)):
        with Locations(Location((-60, 55, 0), (0, 0, 270))):
            Circle(SKETCH14_R)
        with Locations(Location((60, 225, 0), (0, 0, 270))):
            Circle(SKETCH14_R)
    extrude(amount=-CUT_EXTRUDE8_DEPTH, mode=Mode.SUBTRACT)


solid = part.part
